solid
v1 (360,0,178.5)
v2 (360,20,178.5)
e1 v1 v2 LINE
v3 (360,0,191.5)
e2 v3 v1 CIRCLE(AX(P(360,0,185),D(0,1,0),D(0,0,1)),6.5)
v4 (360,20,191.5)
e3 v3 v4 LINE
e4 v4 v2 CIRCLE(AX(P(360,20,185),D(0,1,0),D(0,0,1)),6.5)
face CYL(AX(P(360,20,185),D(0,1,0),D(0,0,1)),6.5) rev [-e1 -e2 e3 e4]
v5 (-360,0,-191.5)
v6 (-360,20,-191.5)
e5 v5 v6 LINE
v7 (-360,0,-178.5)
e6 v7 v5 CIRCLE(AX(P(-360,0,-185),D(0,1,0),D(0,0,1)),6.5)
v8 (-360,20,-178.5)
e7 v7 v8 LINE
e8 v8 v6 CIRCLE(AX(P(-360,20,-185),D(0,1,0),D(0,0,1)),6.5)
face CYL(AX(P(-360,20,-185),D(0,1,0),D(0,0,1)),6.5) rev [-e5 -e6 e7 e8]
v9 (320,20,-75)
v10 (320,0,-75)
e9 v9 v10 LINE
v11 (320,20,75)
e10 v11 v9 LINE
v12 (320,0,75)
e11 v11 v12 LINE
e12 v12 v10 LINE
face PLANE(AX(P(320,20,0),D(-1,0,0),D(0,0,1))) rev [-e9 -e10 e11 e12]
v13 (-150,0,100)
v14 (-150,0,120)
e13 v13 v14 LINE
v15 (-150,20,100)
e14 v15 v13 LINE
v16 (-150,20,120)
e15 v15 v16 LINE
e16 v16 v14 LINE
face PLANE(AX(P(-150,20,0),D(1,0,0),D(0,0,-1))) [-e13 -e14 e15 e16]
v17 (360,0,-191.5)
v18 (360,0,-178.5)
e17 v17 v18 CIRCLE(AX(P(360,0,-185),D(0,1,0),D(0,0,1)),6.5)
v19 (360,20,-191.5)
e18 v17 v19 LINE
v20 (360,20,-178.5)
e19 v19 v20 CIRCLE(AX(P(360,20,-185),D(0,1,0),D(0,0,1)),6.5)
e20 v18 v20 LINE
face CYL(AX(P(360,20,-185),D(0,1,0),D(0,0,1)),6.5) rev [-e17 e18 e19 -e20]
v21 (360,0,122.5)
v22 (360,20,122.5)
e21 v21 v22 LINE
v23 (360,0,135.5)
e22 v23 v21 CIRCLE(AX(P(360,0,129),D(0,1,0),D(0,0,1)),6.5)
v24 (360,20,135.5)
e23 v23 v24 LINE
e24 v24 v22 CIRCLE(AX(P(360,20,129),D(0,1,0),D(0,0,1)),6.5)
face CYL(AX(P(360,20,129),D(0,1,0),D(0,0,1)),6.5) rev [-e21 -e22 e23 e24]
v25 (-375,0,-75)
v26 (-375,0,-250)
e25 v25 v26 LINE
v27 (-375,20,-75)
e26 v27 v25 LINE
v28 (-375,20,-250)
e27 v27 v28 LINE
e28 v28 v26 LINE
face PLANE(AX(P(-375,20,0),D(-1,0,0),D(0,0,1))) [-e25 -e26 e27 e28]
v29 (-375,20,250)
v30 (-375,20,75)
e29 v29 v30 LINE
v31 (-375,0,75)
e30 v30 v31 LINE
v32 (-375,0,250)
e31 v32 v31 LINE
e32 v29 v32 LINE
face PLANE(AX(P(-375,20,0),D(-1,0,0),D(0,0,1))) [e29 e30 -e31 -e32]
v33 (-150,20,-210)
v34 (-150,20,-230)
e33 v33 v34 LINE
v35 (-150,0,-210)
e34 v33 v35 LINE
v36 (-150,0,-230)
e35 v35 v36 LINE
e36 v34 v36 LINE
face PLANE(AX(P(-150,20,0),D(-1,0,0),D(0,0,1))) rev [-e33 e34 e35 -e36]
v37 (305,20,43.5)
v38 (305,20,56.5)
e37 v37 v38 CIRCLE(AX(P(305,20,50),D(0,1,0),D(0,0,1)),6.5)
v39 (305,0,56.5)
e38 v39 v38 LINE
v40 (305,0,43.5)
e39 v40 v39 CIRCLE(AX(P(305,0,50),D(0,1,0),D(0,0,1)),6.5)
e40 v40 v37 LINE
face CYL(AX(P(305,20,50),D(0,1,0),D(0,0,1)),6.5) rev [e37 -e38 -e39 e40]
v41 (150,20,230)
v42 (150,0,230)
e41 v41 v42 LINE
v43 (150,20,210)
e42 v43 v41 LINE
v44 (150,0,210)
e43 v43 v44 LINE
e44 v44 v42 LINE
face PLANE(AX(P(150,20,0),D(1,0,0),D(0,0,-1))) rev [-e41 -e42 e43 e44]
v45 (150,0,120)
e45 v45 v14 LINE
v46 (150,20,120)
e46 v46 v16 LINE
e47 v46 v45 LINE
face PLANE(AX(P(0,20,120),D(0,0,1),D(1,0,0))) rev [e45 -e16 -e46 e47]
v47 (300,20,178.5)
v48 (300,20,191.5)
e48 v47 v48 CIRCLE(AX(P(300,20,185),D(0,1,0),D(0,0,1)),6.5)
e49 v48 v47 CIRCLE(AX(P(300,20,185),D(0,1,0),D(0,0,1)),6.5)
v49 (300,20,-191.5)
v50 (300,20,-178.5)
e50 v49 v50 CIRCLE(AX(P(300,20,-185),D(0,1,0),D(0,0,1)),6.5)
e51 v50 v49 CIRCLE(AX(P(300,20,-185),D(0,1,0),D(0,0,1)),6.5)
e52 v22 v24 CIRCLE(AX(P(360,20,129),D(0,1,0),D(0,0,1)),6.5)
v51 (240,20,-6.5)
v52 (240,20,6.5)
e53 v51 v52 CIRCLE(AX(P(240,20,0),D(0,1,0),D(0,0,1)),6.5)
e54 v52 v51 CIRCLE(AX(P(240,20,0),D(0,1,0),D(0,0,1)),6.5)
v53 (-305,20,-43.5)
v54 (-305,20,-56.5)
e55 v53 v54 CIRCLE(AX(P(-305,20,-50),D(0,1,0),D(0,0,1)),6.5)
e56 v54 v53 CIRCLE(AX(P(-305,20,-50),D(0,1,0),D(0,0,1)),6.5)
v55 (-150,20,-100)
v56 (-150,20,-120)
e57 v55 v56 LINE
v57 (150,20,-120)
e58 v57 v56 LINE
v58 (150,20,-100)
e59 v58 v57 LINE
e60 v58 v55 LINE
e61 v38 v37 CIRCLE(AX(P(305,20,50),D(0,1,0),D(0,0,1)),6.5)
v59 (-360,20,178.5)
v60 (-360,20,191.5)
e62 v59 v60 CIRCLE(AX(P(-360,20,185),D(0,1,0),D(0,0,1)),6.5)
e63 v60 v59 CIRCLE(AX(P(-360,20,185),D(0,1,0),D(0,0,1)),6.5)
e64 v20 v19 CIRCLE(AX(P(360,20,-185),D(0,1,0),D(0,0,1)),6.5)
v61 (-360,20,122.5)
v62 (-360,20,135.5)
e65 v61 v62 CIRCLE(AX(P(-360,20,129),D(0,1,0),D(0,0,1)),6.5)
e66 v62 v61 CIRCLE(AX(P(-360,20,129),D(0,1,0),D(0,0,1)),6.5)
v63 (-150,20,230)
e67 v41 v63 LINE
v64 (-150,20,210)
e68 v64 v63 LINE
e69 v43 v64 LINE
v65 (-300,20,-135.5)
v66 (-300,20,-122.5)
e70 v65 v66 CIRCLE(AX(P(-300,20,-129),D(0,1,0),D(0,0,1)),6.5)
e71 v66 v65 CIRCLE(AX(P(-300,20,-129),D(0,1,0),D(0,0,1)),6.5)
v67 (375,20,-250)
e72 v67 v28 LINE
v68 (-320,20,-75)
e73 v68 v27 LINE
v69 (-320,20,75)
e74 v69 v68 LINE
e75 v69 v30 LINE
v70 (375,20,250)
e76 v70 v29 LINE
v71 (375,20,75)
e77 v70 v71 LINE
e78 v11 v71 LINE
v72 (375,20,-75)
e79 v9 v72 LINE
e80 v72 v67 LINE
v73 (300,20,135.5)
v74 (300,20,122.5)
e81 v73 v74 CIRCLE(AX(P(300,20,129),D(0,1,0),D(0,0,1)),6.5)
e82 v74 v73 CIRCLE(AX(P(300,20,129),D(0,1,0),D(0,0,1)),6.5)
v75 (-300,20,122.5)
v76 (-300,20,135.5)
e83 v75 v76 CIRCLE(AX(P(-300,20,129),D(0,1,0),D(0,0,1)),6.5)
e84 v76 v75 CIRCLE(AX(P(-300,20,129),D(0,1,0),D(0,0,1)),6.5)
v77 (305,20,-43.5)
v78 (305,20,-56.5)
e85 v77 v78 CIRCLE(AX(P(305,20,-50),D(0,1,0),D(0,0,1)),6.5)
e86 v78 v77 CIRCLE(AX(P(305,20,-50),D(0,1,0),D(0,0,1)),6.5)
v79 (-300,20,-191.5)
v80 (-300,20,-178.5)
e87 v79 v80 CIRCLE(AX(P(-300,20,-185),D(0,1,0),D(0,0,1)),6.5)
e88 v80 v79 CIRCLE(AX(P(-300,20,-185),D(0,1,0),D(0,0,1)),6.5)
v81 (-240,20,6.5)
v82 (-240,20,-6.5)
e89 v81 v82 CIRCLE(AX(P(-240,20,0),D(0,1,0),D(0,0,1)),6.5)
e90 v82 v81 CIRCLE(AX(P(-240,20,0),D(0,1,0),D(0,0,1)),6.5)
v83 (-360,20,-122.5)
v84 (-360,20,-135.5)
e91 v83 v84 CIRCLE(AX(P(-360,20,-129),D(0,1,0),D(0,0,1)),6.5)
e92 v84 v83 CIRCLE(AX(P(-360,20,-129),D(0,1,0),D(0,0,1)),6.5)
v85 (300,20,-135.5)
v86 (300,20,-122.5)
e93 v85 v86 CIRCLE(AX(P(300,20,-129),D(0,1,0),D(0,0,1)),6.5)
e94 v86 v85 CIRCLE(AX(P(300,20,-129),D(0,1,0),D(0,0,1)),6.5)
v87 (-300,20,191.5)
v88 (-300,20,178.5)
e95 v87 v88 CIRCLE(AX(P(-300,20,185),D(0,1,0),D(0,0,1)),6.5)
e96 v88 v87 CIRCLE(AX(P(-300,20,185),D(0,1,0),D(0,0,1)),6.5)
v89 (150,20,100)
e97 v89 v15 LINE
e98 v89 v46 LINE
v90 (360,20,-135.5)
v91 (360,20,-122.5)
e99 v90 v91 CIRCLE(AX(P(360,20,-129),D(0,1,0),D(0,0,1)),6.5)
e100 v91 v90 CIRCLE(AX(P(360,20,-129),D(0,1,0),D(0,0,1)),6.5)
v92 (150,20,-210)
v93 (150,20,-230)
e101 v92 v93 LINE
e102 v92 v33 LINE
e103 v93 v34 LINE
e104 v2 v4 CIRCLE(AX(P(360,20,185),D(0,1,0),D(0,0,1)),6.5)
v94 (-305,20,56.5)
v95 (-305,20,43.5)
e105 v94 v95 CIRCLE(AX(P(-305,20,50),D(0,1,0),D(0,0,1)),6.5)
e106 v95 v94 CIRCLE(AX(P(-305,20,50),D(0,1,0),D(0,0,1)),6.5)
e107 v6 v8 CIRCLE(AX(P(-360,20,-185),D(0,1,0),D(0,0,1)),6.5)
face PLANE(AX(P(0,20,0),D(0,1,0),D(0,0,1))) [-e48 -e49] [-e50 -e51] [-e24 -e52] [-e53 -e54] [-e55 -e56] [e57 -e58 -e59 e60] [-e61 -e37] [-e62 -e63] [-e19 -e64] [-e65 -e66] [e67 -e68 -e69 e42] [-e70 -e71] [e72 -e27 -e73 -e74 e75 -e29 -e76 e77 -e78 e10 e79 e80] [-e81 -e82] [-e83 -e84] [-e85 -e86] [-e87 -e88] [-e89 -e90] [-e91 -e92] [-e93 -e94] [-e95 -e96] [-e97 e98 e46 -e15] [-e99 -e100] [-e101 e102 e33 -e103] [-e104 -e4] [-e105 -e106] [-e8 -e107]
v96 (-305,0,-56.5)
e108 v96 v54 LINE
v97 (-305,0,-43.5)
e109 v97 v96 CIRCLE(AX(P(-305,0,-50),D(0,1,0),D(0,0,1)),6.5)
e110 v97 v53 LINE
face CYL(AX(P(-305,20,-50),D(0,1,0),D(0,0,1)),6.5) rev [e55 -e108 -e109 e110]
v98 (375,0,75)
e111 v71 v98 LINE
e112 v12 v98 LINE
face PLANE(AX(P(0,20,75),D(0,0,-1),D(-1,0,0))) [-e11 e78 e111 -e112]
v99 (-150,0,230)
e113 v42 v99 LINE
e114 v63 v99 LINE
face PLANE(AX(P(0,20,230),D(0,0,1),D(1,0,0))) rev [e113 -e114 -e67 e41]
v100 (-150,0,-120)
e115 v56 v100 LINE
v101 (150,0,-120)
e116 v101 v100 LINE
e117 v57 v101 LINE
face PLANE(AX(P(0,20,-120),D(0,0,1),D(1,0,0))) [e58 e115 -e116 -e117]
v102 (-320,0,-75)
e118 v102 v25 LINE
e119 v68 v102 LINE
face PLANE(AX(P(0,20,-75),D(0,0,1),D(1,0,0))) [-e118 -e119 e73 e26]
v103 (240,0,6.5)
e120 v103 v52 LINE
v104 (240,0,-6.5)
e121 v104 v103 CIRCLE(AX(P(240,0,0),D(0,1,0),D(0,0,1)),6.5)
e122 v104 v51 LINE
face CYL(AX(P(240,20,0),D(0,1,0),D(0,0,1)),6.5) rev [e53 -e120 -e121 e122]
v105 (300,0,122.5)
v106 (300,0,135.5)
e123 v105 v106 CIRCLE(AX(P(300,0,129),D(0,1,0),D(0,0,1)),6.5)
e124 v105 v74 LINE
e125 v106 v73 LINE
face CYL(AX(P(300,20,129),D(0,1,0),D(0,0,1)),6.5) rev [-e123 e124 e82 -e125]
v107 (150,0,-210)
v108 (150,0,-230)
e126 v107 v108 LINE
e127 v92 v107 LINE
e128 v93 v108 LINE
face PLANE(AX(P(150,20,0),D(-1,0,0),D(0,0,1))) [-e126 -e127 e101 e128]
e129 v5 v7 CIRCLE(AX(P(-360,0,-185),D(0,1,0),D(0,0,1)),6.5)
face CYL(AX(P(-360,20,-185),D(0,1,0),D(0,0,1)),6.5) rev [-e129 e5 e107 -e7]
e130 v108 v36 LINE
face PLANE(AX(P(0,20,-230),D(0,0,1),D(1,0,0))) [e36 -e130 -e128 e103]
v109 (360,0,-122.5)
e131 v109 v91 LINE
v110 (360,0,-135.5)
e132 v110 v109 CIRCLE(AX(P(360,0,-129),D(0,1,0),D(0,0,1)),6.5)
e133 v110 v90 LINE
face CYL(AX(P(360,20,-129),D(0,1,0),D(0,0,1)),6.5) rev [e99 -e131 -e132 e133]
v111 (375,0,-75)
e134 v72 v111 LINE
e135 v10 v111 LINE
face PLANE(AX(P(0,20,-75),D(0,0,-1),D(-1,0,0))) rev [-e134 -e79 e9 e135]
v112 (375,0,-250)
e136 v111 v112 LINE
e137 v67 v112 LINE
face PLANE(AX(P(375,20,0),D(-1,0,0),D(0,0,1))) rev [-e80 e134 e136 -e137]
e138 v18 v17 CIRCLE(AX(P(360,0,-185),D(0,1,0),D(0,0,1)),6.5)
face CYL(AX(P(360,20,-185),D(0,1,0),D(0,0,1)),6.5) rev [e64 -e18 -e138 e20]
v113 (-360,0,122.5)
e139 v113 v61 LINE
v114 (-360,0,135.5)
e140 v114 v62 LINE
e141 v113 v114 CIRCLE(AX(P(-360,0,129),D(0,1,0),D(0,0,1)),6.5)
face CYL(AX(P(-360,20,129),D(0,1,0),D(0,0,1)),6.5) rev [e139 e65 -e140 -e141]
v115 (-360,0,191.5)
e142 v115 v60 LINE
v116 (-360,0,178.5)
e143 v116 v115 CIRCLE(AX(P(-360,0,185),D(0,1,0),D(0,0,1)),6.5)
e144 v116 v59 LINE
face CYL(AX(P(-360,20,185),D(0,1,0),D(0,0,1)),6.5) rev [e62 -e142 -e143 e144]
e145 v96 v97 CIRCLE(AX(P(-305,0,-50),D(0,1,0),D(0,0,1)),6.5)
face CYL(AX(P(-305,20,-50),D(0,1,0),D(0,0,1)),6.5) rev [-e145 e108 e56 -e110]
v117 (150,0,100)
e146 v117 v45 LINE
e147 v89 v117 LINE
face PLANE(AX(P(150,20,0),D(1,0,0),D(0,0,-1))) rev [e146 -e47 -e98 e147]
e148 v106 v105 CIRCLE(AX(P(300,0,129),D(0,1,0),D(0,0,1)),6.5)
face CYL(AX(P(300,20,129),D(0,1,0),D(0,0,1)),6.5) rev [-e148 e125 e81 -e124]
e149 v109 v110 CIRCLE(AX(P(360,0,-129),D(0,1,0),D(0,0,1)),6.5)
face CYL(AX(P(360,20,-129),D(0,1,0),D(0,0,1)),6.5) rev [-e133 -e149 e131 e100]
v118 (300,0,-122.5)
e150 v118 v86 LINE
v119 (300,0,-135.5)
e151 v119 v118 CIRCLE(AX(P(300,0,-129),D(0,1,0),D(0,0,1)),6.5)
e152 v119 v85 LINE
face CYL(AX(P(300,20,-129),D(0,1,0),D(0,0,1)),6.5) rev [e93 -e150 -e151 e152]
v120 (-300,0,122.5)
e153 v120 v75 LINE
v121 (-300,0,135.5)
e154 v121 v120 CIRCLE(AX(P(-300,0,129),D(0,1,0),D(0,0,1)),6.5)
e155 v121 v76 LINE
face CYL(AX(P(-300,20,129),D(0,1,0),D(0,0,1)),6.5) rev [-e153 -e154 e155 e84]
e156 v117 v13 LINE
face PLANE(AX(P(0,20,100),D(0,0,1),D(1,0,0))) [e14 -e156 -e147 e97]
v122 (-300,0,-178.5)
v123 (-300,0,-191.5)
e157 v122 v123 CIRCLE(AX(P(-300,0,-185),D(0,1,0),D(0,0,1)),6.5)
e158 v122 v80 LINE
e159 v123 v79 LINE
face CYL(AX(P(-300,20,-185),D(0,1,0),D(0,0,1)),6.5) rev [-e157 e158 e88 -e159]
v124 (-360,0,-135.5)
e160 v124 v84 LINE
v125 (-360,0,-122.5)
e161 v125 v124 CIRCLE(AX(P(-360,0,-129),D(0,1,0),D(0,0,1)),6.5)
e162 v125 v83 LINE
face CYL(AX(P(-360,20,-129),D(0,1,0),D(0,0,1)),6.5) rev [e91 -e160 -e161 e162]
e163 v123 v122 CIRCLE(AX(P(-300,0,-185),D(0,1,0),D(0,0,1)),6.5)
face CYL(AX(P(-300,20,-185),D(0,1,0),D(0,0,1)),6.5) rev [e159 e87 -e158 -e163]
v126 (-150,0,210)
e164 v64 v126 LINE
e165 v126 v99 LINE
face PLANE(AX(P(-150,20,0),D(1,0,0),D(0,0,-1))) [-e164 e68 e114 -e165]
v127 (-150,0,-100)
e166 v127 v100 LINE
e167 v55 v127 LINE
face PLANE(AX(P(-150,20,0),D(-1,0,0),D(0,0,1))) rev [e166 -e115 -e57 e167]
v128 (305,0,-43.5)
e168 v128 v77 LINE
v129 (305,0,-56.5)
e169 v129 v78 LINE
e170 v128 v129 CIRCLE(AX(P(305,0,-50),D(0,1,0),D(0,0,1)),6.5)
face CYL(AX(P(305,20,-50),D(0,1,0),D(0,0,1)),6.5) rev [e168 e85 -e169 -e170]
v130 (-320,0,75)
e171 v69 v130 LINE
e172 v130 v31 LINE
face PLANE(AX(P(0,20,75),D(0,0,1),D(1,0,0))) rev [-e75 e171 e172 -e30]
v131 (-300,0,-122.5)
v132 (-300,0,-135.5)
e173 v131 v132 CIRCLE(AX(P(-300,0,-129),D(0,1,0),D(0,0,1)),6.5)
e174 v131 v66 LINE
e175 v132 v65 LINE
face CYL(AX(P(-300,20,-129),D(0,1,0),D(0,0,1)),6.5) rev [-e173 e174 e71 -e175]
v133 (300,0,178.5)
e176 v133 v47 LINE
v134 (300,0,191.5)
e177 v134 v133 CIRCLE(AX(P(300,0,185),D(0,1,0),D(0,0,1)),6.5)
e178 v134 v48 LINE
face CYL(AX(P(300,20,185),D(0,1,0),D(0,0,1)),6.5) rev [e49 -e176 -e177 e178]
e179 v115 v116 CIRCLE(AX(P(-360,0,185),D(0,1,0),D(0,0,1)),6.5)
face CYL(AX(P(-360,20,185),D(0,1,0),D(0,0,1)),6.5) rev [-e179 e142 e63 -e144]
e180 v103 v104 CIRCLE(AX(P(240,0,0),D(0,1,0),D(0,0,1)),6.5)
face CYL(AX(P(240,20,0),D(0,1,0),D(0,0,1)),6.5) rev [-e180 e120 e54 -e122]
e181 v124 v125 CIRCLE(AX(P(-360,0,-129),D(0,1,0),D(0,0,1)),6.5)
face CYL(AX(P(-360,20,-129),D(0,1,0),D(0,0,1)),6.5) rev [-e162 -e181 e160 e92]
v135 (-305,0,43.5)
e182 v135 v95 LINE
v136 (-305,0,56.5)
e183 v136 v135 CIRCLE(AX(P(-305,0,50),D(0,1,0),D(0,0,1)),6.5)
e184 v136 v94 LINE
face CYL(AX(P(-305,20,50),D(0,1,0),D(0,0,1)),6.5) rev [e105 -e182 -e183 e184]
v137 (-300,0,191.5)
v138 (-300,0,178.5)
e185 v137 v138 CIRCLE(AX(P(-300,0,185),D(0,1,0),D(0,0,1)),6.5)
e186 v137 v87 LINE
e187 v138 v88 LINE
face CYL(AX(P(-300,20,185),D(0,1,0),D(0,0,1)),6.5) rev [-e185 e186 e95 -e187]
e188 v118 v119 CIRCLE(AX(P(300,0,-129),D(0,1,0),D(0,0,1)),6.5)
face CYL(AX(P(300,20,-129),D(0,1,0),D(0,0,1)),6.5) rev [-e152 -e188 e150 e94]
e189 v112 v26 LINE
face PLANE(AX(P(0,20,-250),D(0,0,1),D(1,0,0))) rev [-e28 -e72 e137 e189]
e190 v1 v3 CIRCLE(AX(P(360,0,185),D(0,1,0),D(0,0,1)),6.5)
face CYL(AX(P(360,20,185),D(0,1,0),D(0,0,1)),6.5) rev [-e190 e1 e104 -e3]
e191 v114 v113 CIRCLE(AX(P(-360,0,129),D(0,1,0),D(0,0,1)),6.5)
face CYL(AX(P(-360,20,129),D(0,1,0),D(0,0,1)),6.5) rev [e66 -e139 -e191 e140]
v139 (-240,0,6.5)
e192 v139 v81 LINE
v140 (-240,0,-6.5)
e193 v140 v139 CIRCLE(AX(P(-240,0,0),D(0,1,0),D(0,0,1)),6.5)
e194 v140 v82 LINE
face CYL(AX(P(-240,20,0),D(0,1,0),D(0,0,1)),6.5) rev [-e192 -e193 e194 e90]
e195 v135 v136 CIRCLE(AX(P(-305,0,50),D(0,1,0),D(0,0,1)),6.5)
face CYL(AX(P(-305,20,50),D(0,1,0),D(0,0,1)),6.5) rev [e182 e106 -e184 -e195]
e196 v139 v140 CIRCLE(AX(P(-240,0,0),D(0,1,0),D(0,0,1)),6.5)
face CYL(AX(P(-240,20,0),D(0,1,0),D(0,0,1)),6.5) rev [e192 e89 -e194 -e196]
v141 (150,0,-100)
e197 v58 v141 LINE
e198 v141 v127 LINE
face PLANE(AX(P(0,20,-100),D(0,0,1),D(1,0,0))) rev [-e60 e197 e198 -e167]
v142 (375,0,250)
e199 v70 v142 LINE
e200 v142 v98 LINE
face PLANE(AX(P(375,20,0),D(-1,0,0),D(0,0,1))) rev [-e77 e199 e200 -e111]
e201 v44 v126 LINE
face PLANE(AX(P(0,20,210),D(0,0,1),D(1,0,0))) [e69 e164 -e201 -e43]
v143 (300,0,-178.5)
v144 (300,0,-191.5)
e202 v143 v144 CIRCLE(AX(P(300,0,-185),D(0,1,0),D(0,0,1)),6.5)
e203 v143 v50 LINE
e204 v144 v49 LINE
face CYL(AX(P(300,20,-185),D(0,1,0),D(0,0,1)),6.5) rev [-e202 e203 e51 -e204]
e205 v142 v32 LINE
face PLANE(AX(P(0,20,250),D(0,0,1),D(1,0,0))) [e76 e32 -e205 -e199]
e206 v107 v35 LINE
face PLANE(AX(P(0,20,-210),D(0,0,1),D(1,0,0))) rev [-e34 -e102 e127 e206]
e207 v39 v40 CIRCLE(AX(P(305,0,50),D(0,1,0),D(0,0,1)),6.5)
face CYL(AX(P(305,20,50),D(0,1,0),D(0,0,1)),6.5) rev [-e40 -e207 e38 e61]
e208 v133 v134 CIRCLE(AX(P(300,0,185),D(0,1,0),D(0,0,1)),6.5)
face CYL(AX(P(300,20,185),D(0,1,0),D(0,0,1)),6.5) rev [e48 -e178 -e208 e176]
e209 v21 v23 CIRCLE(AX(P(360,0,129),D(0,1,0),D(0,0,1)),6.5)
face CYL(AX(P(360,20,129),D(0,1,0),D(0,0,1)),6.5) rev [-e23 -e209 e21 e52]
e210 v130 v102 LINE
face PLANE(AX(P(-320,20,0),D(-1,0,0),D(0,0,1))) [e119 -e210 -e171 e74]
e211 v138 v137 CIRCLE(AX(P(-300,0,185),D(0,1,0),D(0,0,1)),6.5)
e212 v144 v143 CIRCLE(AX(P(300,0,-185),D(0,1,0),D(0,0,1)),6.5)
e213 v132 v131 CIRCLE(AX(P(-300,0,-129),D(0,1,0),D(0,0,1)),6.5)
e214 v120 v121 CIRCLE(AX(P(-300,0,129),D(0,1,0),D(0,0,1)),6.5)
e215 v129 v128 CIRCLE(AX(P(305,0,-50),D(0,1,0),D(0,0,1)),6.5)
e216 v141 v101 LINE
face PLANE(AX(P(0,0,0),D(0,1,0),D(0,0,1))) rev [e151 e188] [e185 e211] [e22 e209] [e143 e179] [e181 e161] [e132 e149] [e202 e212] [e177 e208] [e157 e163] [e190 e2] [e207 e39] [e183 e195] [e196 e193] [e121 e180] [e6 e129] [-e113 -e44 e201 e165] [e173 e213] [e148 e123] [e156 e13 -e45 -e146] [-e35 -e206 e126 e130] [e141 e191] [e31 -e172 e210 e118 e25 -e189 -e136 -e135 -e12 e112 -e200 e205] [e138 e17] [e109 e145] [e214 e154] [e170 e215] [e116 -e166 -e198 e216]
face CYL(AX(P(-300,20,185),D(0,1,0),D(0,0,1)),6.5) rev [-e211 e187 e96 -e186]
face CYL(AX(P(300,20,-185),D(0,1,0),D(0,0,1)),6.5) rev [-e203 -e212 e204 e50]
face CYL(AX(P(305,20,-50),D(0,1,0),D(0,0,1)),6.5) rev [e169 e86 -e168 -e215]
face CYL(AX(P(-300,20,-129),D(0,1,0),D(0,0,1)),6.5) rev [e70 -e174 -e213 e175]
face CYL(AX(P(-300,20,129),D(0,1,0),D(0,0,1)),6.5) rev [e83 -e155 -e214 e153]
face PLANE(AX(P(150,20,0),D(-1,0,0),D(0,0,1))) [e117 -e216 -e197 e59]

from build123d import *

# Parameters (mm, degrees)
SKETCH1_W                  = 300
SKETCH1_H                  = 20
BOSS_EXTRUDE1_DEPTH        = 20
F_13_0_13_DIAMETER_HOLE1_D = 13


with BuildPart() as part:
    # Sketch1 → Boss-Extrude1 (new body)
    with BuildSketch(Plane(origin=(0, 0, 0), x_dir=(1, 0, 0), z_dir=(0, 1, 0))):
        Polygon((-375, -250), (375, -250), (375, -75), (320, -75), (320, 75), (375, 75), (375, 250), (-375, 250), (-375, 75), (-320, 75), (-320, -75), (-375, -75), align=None)
        with Locations((0, -220)):
            Rectangle(SKETCH1_W, SKETCH1_H, mode=Mode.SUBTRACT)
        with Locations((0, -110)):
            Rectangle(SKETCH1_W, SKETCH1_H, mode=Mode.SUBTRACT)
        with Locations((0, 110)):
            Rectangle(SKETCH1_W, SKETCH1_H, mode=Mode.SUBTRACT)
        with Locations((0, 220)):
            Rectangle(SKETCH1_W, SKETCH1_H, mode=Mode.SUBTRACT)
    extrude(amount=BOSS_EXTRUDE1_DEPTH)

    # Ø13.0 (13) Diameter Hole1 (through all)
    with Locations(Plane(origin=(0, 20, 0), x_dir=(1, 0, 0), z_dir=(0, 1, 0))):
        with Locations((-360, 129), (-305, 50), (-240, 0), (-300, 129), (-300, 185), (-360, 185), (-360, -129), (-360, -185), (-300, -129), (-300, -185), (-305, -50), (360, -129), (300, -129), (360, -185), (360, 129), (360, 185), (300, 129), (305, -50), (300, -185), (300, 185), (240, 0), (305, 50)):
            Hole(F_13_0_13_DIAMETER_HOLE1_D / 2)


solid = part.part
